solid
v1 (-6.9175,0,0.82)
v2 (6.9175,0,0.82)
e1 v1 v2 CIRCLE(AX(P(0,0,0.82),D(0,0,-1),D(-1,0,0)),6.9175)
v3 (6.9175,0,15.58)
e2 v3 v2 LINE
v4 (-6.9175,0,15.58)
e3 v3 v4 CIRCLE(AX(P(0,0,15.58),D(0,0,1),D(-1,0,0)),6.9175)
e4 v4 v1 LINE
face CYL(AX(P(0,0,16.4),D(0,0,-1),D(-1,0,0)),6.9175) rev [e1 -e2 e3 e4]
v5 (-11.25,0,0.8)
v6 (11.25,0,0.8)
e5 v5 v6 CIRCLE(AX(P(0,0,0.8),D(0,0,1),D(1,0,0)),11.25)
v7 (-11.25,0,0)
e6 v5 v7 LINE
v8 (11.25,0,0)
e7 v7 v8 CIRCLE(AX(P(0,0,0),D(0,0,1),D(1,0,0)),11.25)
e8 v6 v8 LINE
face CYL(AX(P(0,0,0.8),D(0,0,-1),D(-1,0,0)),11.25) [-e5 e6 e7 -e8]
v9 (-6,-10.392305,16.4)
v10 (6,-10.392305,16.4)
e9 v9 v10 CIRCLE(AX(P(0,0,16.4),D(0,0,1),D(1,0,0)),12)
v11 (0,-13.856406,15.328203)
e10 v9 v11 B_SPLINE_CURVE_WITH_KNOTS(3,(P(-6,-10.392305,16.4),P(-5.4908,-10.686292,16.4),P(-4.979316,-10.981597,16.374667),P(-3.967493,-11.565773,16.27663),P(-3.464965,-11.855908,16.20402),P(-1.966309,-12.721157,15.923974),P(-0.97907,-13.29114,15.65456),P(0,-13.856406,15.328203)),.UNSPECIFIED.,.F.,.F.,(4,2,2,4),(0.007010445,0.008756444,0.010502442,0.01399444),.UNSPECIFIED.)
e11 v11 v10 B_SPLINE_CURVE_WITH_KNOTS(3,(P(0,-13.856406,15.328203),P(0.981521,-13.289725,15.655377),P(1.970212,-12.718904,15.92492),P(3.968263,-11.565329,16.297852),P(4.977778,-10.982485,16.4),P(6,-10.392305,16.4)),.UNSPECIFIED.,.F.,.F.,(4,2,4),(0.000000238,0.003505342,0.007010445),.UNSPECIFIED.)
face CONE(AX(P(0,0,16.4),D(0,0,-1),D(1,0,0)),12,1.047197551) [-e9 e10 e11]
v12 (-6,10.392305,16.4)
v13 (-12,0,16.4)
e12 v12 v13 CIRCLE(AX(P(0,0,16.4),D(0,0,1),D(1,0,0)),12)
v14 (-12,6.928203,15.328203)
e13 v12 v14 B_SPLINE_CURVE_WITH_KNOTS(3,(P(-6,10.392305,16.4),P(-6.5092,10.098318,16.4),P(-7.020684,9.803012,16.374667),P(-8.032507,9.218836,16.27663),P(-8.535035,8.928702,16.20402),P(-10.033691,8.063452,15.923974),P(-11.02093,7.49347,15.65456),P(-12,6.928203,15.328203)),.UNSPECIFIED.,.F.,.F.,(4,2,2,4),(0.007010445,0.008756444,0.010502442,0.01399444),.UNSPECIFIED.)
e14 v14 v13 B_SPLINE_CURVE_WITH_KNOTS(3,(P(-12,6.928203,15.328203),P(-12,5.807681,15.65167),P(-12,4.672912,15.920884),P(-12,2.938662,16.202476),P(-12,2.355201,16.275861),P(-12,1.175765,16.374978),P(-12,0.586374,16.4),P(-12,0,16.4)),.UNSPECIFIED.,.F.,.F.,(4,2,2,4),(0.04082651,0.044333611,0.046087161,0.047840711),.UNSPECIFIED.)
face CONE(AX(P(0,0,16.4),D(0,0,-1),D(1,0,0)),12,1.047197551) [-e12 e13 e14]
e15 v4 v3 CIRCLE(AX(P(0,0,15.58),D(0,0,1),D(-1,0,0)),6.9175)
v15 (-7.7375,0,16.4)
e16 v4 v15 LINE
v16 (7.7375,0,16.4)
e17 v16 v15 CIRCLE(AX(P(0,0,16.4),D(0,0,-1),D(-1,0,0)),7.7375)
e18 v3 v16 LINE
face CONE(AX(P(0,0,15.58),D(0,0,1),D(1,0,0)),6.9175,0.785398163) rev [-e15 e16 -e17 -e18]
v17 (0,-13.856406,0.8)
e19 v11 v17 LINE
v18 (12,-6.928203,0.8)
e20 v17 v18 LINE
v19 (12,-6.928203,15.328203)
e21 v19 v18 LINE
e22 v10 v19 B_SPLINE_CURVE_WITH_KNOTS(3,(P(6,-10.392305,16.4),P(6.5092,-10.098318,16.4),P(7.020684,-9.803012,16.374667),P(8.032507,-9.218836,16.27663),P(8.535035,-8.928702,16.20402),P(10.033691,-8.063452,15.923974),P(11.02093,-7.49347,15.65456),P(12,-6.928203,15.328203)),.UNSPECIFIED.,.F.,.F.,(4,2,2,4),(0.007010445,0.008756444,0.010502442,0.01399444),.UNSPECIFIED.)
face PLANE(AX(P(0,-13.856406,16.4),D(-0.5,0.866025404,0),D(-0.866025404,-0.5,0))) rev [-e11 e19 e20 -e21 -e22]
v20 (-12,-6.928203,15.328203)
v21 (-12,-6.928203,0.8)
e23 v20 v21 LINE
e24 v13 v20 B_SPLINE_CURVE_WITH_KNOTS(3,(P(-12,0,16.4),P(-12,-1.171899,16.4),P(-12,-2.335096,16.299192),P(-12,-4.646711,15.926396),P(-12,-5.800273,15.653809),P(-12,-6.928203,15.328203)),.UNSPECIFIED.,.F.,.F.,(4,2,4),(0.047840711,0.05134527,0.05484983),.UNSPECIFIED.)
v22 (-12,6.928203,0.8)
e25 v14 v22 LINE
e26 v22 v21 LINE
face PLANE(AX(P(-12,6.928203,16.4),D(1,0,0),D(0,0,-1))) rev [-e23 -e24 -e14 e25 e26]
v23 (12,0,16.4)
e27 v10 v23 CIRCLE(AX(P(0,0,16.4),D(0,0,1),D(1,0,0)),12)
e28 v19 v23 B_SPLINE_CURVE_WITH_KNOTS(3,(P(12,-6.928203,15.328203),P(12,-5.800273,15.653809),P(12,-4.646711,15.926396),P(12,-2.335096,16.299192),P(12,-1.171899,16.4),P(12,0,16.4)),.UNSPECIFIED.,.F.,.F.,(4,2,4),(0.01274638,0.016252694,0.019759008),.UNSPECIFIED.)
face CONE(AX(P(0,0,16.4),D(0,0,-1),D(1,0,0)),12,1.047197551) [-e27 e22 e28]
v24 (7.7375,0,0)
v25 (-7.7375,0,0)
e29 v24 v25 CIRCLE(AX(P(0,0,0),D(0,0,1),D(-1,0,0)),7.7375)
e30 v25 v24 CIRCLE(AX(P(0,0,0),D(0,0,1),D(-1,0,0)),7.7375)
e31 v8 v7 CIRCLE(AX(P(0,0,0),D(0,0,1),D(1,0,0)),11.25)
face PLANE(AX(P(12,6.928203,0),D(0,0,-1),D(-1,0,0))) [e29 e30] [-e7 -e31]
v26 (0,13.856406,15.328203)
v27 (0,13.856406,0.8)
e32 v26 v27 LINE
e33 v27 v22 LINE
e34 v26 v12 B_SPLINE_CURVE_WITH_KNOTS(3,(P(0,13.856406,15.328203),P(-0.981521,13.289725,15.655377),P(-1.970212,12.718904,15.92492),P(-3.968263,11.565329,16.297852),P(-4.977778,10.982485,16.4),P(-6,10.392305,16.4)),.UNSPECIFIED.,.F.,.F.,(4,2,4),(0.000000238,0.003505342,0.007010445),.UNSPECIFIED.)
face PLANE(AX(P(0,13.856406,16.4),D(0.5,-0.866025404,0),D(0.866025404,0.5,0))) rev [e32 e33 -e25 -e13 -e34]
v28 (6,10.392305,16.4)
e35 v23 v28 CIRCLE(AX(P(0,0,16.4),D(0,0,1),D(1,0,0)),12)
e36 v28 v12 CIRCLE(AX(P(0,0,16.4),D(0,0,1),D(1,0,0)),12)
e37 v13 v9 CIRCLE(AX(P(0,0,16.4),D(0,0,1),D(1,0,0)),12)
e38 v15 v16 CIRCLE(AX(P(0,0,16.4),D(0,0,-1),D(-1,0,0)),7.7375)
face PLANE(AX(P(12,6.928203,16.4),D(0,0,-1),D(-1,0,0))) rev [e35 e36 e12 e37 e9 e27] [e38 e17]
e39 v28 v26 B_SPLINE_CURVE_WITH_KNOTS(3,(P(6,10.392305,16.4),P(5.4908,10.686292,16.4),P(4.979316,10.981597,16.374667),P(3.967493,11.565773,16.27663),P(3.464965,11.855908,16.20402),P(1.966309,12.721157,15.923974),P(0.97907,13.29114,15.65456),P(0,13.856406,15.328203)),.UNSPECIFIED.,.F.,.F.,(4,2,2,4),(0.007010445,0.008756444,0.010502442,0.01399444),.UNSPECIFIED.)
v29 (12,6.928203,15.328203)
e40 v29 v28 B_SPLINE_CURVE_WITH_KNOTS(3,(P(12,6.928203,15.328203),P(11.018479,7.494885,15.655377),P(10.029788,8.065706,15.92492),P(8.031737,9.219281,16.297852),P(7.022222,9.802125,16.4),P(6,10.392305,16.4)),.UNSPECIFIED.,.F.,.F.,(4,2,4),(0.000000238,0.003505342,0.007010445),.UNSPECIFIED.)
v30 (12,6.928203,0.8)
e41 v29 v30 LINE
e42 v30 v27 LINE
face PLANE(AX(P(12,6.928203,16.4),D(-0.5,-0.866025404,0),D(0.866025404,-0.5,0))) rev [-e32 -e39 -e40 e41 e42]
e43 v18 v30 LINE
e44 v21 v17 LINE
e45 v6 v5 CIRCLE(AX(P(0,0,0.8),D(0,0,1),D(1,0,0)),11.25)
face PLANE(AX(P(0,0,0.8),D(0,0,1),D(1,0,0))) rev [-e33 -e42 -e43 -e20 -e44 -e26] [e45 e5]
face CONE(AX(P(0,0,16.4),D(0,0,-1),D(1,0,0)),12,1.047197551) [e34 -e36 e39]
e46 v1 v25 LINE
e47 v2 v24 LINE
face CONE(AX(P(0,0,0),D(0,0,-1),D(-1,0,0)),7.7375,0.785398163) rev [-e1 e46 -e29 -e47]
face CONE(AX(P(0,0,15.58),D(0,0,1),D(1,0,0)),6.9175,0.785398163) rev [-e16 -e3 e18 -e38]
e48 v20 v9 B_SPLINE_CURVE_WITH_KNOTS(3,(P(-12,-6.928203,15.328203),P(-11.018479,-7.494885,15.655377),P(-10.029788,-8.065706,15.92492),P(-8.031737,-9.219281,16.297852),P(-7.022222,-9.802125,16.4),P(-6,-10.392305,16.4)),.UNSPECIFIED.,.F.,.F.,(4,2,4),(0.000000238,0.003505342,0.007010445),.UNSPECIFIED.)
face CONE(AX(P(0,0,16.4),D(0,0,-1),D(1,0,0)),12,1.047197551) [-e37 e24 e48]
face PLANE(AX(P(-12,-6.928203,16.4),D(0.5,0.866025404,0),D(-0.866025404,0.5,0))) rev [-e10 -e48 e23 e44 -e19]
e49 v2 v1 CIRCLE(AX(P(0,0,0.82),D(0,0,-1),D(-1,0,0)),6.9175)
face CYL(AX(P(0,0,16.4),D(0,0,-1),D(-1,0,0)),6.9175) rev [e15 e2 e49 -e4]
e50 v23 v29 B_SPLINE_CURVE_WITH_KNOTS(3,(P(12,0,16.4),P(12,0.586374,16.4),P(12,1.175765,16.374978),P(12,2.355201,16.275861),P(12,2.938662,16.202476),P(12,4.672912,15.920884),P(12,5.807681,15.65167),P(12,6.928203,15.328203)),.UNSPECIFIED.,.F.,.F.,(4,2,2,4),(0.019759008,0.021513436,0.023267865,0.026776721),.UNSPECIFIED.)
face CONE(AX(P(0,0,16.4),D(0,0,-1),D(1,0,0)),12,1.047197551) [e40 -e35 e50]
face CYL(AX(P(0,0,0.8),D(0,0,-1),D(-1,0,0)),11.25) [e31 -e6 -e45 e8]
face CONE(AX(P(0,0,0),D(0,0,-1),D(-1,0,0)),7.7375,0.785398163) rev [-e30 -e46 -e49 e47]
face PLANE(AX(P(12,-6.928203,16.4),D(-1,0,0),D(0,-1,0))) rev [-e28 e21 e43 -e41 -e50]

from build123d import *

# Parameters (mm, degrees)
SKETCH1_R          = 6.9175
EXTRUDE1_DEPTH     = 16.4
SKETCH2_OUTSIDE_W  = 34.032
SKETCH2_OUTSIDE_H  = 37.744
SKETCH2_OUTSIDE_R  = 11.25
CUT_EXTRUDE2_DEPTH = 0.8
SKETCH3_OUTSIDE_W  = 122.7
SKETCH3_OUTSIDE_H  = 126.412
SKETCH3_OUTSIDE_R  = 12
CUT_EXTRUDE3_DEPTH = 25.595934623
CUT_EXTRUDE3_DRAFT = -60
CHAMFER1_SIZE      = 0.82


with BuildPart() as part:
    # Sketch1 → Extrude1 (new body)
    with BuildSketch(Plane.XY):
        Polygon((0, 13.856406461), (-12, 6.92820323), (-12, -6.92820323), (0, -13.856406461), (12, -6.92820323), (12, 6.92820323), align=None)
        Circle(SKETCH1_R, mode=Mode.SUBTRACT)
    extrude(amount=EXTRUDE1_DEPTH)

    # Sketch2 outside → Cut-Extrude2 (cut)
    with BuildSketch(Plane.XY):
        Rectangle(SKETCH2_OUTSIDE_W, SKETCH2_OUTSIDE_H)
        Circle(SKETCH2_OUTSIDE_R, mode=Mode.SUBTRACT)
    extrude(amount=CUT_EXTRUDE2_DEPTH, mode=Mode.SUBTRACT)


with BuildPart() as cut_extrude3_tool:
    # Sketch3 outside → Cut-Extrude3 (with draft: the straight prism first)
    with BuildSketch(Plane.XY.offset(16.4)):
        Rectangle(SKETCH3_OUTSIDE_W, SKETCH3_OUTSIDE_H)
        Circle(SKETCH3_OUTSIDE_R, mode=Mode.SUBTRACT)
    extrude(amount=-CUT_EXTRUDE3_DEPTH)
    # Cut-Extrude3: the draft: its side faces are tilted about the plane it starts from
    cut_extrude3_sides = [cut_extrude3_tool.faces().sort_by_distance(p)[0] for p in [
        (0, -63.206, 3.602032688),
        (61.35, 0, 3.602032688),
        (0, 63.206, 3.602032688),
        (-61.35, 0, 3.602032688),
        (-12, 0, 3.602032688),
    ]]
    draft(cut_extrude3_sides, Plane.XY.offset(16.4), CUT_EXTRUDE3_DRAFT)


with BuildPart() as part_1:
    add(part.part)

    # Cut-Extrude3: cut by cut_extrude3_tool
    add(cut_extrude3_tool.part, mode=Mode.SUBTRACT)

    # Chamfer1
    chamfer1_edges = [part_1.edges().sort_by_distance(p)[0] for p in [
        (-6.9175, 0, 0),
        (-6.9175, 0, 16.4),
    ]]
    chamfer(chamfer1_edges, length=CHAMFER1_SIZE)


solid = part_1.part
